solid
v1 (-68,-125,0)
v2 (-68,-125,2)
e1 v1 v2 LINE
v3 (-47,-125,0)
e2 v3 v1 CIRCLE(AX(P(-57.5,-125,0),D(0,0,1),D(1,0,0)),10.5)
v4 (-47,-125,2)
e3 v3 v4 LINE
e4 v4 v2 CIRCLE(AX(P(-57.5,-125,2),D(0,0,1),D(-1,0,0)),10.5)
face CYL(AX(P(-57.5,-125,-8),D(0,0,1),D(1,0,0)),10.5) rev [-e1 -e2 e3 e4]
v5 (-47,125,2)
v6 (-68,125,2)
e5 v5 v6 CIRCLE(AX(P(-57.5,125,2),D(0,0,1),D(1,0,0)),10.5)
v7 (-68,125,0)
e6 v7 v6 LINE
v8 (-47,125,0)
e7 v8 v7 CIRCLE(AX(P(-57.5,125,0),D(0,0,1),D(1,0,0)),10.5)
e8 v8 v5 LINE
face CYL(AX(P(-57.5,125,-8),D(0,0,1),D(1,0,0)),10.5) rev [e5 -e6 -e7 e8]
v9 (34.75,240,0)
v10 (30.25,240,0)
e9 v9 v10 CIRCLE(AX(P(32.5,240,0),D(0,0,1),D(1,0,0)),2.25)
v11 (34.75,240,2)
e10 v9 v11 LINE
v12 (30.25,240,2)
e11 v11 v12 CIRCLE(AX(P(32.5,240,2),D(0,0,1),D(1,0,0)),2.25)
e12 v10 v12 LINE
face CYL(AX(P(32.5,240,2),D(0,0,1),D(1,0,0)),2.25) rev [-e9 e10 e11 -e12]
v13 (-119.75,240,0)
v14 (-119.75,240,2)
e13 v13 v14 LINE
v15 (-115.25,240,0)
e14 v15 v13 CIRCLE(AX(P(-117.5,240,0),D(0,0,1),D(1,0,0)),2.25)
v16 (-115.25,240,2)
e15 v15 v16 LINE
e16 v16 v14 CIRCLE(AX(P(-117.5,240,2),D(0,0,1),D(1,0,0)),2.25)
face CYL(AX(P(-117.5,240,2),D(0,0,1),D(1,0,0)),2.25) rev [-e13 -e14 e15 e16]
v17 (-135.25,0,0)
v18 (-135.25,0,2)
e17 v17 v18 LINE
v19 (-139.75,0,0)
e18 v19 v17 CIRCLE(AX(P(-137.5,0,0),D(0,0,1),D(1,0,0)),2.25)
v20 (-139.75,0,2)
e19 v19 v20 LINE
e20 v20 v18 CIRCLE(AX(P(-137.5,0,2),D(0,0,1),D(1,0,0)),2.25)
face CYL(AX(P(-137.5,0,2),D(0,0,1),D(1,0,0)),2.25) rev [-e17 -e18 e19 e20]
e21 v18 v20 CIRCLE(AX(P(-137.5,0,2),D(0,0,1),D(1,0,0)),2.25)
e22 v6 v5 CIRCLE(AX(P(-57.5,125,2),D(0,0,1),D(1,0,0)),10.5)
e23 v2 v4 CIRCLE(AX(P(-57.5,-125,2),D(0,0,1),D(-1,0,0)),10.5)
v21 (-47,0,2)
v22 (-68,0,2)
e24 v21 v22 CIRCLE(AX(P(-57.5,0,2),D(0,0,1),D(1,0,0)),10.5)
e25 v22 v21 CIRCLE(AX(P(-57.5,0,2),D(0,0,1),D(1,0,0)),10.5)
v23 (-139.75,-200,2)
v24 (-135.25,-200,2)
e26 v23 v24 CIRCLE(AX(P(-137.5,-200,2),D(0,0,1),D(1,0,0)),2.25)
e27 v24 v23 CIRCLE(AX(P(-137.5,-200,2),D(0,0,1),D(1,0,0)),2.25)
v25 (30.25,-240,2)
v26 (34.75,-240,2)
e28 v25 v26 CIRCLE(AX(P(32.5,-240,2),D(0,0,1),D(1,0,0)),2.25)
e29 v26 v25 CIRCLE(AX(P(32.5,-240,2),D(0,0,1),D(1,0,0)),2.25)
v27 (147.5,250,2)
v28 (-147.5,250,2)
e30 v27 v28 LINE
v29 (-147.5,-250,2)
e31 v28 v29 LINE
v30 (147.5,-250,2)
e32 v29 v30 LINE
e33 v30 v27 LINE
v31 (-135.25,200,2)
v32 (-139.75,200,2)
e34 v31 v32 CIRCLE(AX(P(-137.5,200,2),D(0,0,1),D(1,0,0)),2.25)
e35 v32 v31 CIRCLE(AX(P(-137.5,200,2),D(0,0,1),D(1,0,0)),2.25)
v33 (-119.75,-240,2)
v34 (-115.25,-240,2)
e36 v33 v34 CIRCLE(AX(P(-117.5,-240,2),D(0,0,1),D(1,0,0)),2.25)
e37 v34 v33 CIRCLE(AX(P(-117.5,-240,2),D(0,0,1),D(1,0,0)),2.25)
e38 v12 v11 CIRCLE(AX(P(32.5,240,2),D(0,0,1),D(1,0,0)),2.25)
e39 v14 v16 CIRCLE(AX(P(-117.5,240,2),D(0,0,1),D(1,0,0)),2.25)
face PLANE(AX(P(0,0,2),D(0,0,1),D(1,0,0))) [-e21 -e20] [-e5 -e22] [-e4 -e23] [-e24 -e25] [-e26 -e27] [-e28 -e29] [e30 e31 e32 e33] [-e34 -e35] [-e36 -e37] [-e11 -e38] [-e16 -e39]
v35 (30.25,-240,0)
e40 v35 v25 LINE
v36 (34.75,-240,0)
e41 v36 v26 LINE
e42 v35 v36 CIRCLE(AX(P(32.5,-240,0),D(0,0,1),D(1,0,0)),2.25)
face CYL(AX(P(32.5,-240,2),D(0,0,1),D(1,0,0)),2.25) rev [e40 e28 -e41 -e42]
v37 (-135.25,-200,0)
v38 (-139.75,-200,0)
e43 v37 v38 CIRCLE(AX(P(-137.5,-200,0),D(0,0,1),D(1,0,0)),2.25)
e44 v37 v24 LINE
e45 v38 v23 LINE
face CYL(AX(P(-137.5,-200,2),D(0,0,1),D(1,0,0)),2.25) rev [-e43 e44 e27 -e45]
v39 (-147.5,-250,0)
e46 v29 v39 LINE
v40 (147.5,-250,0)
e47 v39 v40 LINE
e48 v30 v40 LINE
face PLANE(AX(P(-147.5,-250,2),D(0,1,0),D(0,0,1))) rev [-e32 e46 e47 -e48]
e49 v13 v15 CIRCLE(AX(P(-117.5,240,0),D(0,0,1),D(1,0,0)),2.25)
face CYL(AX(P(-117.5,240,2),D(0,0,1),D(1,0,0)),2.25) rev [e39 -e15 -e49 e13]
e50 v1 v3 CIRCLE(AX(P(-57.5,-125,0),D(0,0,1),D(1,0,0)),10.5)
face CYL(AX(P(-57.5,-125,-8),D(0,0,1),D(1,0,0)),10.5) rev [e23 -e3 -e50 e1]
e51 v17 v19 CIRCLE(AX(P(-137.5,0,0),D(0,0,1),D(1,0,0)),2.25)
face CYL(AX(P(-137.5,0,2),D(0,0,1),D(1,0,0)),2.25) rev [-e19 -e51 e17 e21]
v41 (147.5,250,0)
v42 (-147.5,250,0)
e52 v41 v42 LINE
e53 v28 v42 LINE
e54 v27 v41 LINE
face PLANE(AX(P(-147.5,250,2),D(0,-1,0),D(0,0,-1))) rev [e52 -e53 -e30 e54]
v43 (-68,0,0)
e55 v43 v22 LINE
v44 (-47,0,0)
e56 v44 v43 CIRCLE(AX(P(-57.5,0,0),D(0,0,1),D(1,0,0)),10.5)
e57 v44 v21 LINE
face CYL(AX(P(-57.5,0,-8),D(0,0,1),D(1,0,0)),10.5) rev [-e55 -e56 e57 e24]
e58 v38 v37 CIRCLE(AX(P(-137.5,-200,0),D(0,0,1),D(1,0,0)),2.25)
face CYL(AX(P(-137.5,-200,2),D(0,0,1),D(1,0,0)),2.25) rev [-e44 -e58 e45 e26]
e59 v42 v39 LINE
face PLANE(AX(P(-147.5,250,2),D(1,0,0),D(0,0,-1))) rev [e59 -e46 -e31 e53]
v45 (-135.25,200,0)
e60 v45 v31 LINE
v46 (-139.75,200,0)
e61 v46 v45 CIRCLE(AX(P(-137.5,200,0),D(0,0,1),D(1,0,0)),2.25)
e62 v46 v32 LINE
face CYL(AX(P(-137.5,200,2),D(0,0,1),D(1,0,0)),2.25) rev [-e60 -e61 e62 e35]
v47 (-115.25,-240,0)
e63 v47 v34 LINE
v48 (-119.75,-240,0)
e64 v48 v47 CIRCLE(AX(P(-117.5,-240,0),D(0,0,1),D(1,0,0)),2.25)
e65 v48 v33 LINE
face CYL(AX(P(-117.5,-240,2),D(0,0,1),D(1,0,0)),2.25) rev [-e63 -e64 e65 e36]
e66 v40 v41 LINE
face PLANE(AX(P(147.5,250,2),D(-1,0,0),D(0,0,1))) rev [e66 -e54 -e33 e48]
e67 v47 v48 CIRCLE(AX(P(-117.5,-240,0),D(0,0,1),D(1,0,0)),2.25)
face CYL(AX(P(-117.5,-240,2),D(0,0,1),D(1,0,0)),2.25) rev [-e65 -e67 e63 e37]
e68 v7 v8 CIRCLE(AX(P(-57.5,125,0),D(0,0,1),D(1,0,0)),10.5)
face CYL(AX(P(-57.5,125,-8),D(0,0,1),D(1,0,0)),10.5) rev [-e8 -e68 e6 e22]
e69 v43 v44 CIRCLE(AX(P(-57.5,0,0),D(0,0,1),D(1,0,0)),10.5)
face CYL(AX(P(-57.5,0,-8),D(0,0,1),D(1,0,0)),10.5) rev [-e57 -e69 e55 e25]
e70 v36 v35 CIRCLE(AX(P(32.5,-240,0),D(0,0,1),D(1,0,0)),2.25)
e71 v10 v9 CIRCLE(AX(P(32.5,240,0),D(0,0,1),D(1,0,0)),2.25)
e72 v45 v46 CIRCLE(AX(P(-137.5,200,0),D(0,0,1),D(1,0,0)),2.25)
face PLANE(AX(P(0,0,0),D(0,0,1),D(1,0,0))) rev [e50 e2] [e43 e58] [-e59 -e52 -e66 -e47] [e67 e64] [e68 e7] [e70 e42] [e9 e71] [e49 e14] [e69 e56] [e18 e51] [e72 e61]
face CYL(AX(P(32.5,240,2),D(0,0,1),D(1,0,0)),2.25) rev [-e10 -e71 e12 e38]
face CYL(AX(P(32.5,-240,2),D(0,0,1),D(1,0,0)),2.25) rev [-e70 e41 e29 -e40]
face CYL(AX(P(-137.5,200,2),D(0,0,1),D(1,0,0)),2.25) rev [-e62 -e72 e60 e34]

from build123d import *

# Parameters (mm, degrees)
SKETCH_1_W                  = 295
SKETCH_1_H                  = 500
EXTRUDE_1_DEPTH             = 2
HOLE_WIZARD_4_5_4_5_1_D     = 4.5
HOLE_WIZARD_4_5_4_5_1_DEPTH = 8
HOLE_WIZARD_4_5_4_5_1_TIP   = 1.351936393
SKETCH_4_R                  = 10.5
CUT_EXTRUDE_1_DEPTH         = 10


with BuildPart() as part:
    # 草图1 → 凸台-拉伸1 (new body)
    with BuildSketch(Plane.XY):
        Rectangle(SKETCH_1_W, SKETCH_1_H)
    extrude(amount=EXTRUDE_1_DEPTH)

    # Ø4.5 (4.5) 直径孔1
    with Locations(Plane.XY.offset(2)):
        with Locations((-117.5, -240), (-137.5, 0), (-137.5, 200), (-137.5, -200), (-117.5, 240), (32.5, 240), (32.5, -240)):
            Hole(HOLE_WIZARD_4_5_4_5_1_D / 2, depth=HOLE_WIZARD_4_5_4_5_1_DEPTH)
            with Locations((0, 0, -(HOLE_WIZARD_4_5_4_5_1_DEPTH + HOLE_WIZARD_4_5_4_5_1_TIP / 2))):  # 118° drill point
                Cone(0, HOLE_WIZARD_4_5_4_5_1_D / 2, HOLE_WIZARD_4_5_4_5_1_TIP, mode=Mode.SUBTRACT)

    # 草图4 → 切除-拉伸1 (cut)
    with BuildSketch(Plane.XY.offset(2)):
        with Locations((-57.5, 125)):
            Circle(SKETCH_4_R)
        with Locations((-57.5, -125)):
            Circle(SKETCH_4_R)
        with Locations((-57.5, 0)):
            Circle(SKETCH_4_R)
    extrude(amount=-CUT_EXTRUDE_1_DEPTH, mode=Mode.SUBTRACT)


solid = part.part
